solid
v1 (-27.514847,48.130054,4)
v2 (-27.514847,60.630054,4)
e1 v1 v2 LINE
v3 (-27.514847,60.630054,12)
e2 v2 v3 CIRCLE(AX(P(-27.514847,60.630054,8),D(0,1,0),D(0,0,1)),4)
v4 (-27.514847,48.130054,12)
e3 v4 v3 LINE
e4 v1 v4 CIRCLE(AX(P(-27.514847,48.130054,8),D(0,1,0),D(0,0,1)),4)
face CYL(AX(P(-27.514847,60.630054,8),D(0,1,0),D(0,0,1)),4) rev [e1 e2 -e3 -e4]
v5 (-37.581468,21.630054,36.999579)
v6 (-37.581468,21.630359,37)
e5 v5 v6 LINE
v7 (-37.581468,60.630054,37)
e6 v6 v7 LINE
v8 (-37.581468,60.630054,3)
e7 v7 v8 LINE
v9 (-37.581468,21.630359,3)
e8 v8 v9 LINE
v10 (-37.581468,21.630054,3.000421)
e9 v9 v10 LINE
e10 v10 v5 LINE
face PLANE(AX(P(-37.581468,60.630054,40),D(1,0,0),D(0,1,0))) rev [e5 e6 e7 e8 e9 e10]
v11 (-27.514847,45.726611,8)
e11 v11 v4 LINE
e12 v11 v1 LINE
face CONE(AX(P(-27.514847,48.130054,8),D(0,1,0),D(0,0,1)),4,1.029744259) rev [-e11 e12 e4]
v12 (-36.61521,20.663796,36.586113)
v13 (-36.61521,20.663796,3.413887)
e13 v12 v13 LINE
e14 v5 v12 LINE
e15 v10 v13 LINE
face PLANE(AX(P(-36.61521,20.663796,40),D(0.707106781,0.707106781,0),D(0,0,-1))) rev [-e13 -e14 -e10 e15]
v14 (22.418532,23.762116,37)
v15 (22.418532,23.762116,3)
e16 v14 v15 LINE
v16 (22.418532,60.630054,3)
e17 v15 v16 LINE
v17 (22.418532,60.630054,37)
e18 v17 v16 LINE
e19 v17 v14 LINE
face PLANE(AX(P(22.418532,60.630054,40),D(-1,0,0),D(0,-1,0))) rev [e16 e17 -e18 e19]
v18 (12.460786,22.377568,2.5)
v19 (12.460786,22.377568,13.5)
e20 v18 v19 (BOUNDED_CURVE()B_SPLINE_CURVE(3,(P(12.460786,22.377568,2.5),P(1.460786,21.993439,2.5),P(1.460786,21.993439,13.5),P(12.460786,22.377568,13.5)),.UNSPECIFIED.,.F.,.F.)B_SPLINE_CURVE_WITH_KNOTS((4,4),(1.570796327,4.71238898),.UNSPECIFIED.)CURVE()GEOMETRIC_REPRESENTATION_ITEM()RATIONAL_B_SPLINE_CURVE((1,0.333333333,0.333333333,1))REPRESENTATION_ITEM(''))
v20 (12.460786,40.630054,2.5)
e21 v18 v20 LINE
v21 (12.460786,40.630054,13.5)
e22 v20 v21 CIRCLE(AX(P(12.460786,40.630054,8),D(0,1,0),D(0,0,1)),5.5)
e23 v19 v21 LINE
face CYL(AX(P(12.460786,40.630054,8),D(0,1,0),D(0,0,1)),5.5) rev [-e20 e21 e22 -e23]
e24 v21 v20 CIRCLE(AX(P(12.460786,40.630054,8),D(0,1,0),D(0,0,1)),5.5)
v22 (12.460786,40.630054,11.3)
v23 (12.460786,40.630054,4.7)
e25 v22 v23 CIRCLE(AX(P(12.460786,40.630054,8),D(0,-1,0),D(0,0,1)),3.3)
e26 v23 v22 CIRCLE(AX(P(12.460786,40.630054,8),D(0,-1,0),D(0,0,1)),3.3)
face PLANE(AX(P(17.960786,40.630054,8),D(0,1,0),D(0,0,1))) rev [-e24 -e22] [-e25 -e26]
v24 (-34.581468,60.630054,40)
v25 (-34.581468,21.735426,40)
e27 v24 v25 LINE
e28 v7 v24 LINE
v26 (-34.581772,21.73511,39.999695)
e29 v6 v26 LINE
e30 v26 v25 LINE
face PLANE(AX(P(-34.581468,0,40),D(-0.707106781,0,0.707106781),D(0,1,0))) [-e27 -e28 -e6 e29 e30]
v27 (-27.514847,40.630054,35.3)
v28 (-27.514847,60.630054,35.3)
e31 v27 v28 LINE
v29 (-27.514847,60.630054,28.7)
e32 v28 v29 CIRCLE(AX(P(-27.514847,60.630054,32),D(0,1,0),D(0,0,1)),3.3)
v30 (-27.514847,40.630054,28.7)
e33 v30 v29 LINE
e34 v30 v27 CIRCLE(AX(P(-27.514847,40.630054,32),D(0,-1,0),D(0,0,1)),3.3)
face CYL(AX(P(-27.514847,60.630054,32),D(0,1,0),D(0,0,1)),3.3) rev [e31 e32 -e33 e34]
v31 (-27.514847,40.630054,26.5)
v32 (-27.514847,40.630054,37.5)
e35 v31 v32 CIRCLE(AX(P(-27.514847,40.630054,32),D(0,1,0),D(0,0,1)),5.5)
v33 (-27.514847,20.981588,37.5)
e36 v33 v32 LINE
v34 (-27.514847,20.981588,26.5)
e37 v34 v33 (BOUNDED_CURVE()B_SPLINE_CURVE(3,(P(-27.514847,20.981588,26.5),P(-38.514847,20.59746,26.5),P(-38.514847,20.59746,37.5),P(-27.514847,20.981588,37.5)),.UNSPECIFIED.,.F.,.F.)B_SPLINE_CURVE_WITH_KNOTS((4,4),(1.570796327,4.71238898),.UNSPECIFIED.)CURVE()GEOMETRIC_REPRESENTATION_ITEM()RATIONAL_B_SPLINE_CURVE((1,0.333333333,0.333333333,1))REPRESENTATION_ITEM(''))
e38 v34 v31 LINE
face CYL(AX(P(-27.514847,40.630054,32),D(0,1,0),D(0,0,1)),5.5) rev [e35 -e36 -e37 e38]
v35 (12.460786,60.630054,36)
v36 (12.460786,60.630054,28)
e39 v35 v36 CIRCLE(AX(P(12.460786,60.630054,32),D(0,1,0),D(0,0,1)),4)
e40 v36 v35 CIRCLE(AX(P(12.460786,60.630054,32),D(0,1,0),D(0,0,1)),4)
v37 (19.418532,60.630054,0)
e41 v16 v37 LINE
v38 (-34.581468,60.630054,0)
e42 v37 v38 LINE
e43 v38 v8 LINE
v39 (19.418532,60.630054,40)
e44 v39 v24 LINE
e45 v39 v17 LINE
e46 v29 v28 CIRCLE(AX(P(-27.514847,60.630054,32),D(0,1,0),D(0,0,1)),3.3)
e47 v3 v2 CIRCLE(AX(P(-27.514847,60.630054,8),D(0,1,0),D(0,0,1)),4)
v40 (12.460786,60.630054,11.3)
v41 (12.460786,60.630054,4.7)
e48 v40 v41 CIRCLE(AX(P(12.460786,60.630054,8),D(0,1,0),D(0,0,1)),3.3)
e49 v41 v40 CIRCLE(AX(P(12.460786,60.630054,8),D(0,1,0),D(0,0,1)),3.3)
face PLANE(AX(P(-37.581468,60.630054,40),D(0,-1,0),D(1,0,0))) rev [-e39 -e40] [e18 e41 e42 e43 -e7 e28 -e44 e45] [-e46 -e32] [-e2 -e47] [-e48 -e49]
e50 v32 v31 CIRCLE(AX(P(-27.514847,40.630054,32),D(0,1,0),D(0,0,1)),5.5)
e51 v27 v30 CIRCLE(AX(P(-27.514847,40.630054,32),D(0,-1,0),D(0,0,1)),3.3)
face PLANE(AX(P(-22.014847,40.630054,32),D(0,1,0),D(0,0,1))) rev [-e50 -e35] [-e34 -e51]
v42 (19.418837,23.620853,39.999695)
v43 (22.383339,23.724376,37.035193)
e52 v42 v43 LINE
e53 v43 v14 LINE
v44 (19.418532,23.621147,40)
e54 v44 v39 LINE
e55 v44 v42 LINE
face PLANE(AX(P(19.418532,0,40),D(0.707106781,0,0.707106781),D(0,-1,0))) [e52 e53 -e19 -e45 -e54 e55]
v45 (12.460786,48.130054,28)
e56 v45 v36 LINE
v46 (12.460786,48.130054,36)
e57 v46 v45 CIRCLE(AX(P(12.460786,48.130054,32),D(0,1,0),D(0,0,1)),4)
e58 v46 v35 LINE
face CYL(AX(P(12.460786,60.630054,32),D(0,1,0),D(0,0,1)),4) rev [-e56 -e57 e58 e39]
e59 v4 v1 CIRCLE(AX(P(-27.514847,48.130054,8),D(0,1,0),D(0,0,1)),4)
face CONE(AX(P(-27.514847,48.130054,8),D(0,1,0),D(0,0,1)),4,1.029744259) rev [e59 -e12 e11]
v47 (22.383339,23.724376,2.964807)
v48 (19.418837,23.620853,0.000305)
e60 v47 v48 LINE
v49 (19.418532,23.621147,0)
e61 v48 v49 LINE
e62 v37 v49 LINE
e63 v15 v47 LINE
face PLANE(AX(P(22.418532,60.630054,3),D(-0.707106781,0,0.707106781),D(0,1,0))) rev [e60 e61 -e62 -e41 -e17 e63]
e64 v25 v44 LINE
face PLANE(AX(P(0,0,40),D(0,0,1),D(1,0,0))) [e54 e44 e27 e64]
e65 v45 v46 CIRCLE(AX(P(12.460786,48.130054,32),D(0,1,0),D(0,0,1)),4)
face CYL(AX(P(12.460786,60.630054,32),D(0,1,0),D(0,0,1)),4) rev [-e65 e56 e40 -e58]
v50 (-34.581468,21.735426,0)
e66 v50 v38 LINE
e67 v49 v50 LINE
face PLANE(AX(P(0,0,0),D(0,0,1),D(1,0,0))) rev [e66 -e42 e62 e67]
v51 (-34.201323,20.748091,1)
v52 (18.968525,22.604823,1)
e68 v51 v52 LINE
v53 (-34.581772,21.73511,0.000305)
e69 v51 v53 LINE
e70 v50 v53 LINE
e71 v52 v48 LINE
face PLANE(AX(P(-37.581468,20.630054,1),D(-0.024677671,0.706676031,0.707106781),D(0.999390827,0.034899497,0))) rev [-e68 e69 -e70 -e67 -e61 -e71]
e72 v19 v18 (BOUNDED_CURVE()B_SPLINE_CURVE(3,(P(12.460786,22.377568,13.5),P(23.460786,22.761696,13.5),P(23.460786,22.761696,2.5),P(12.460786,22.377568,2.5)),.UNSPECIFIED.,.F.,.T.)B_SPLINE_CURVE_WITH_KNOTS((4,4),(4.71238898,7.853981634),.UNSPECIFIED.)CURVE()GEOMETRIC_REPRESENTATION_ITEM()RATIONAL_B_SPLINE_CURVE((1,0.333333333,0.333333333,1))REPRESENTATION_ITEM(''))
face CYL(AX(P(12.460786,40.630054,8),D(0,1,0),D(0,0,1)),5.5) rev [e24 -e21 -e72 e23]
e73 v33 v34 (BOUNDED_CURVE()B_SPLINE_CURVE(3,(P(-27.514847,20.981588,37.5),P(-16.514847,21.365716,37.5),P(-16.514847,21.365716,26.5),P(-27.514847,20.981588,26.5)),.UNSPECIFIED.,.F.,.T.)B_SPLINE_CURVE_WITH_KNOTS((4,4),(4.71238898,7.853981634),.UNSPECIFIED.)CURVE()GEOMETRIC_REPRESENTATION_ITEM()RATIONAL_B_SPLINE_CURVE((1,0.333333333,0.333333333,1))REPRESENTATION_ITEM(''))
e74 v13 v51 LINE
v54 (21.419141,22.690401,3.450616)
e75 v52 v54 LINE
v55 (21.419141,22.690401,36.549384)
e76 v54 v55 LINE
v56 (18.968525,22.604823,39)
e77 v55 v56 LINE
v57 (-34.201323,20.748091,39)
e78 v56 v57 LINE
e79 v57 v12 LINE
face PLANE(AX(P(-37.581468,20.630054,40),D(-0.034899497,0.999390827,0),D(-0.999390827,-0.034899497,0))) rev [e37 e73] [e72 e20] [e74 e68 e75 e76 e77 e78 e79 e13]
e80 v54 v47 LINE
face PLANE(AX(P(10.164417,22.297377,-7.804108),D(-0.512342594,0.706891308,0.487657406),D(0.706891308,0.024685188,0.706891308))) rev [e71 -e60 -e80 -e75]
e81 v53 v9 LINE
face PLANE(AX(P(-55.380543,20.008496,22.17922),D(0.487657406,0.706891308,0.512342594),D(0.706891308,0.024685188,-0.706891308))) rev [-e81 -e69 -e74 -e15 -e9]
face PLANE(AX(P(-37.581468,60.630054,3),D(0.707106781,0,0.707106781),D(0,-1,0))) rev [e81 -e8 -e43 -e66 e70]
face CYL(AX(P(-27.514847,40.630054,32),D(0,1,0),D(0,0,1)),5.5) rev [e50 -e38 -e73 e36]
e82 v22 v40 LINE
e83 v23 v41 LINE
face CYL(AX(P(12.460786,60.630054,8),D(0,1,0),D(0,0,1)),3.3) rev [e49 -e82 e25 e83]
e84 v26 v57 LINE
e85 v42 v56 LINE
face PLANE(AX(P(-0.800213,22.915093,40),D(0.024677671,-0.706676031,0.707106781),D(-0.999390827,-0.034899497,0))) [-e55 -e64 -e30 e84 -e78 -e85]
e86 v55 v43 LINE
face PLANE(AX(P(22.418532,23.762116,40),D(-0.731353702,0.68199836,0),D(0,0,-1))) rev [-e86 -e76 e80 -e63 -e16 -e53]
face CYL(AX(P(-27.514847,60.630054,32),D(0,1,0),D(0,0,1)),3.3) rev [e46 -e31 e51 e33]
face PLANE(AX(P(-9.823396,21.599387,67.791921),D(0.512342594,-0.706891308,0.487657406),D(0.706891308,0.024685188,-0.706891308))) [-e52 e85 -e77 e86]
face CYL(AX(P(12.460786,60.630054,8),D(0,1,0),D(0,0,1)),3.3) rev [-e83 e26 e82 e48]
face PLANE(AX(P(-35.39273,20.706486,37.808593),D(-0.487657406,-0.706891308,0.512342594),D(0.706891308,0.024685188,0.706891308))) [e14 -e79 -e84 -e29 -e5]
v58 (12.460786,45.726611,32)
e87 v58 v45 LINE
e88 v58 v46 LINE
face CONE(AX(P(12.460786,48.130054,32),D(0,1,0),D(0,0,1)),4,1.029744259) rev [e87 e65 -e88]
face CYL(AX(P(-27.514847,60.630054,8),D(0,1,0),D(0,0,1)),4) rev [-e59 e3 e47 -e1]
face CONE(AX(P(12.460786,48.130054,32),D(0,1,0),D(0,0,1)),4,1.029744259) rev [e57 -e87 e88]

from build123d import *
from OCP.BRepFilletAPI import BRepFilletAPI_MakeChamfer

# Parameters (mm, degrees)
BOSS_EXTRUDE1_DEPTH        = 40
CHAMFER1_SIZE              = 3
CHAMFER2_SIZE              = 1
CHAMFER2_SIZE2             = 0.96684652
CHAMFER2_SIZE2_2           = 1.036815955
CHAMFER2_SIZE2_3           = 0.976206784
CHAMFER2_SIZE2_4           = 1.025622313
HOLE2_D                    = 6.6
HOLE2_DEPTH                = 20
SKETCH11_W                 = 5.5
SKETCH11_H                 = 19.966257543
HOLE3_AT_2_COUNT           = 2
HOLE3_AT_2_PITCH           = 46.626722383
SIZE_MM_BLIND_HOLE_1_D     = 8
SIZE_MM_BLIND_HOLE_1_DEPTH = 12.5
SIZE_MM_BLIND_HOLE_1_TIP   = 2.403442476


with BuildPart() as part:
    # Sketch2 → Boss-Extrude1 (new body)
    with BuildSketch(Plane.XY):
        Polygon((-37.58146769, 20.630053858), (22.41853231, 22.725300027), (22.41853231, 60.630053858), (-37.58146769, 60.630053858), align=None)
    extrude(amount=BOSS_EXTRUDE1_DEPTH)

    # Chamfer1
    chamfer1_edges = [part.edges().sort_by_distance(p)[0] for p in [
        (22.41853231, 41.677676942, 40),
        (-37.58146769, 40.630053858, 40),
        (22.41853231, 41.677676942, 0),
        (-37.58146769, 40.630053858, 0),
    ]]
    chamfer(chamfer1_edges, length=CHAMFER1_SIZE)

    # Chamfer2: one chamfer whose edges measure the first distance from different faces: ONE call of the kernel's chamfer builder (chamfer() names one face for all edges)
    chamfer2_edges_1 = [part.edges().sort_by_distance(p)[0] for p in [
        (-37.58146769, 20.630053858, 20),
    ]]
    chamfer2_side_1 = [part.faces().sort_by_distance(p)[0] for p in [
        (-37.58146769, 40.630053858, 20),
    ]]
    chamfer2_edges_2 = [part.edges().sort_by_distance(p)[0] for p in [
        (-7.58146769, 21.677676942, 0),
        (-7.58146769, 21.677676942, 40),
    ]]
    chamfer2_edges_3 = [part.edges().sort_by_distance(p)[0] for p in [
        (22.41853231, 22.725300027, 20),
    ]]
    chamfer2_side_3 = [part.faces().sort_by_distance(p)[0] for p in [
        (-7.58146769, 21.677676942, 20),
    ]]
    chamfer2_edges_4 = [part.edges().sort_by_distance(p)[0] for p in [
        (-36.08146769, 20.682435012, 38.5),
    ]]
    chamfer2_side_4 = [part.faces().sort_by_distance(p)[0] for p in [
        (-36.082123313, 40.656232987, 38.499344377),
    ]]
    chamfer2_edges_5 = [part.edges().sort_by_distance(p)[0] for p in [
        (20.91853231, 22.672918873, 38.5),
    ]]
    chamfer2_side_5 = [part.faces().sort_by_distance(p)[0] for p in [
        (20.917842306, 41.651474317, 38.500690004),
    ]]
    chamfer2_edges_6 = [part.edges().sort_by_distance(p)[0] for p in [
        (20.91853231, 22.672918873, 1.5),
    ]]
    chamfer2_side_6 = [part.faces().sort_by_distance(p)[0] for p in [
        (20.917842306, 41.651474317, 1.499309996),
    ]]
    chamfer2_edges_7 = [part.edges().sort_by_distance(p)[0] for p in [
        (-36.08146769, 20.682435012, 1.5),
    ]]
    chamfer2_side_7 = [part.faces().sort_by_distance(p)[0] for p in [
        (-36.082123313, 40.656232987, 1.500655623),
    ]]
    chamfer2 = BRepFilletAPI_MakeChamfer(part.part.solid().wrapped)
    for e in chamfer2_edges_1:
        chamfer2.Add(CHAMFER2_SIZE, CHAMFER2_SIZE2, e.wrapped, chamfer2_side_1[0].wrapped)  # the first distance lies on this face
    for e in chamfer2_edges_2:
        chamfer2.Add(CHAMFER2_SIZE, e.wrapped)
    for e in chamfer2_edges_3:
        chamfer2.Add(CHAMFER2_SIZE, CHAMFER2_SIZE2_2, e.wrapped, chamfer2_side_3[0].wrapped)  # the first distance lies on this face
    for e in chamfer2_edges_4:
        chamfer2.Add(CHAMFER2_SIZE, CHAMFER2_SIZE2_3, e.wrapped, chamfer2_side_4[0].wrapped)  # the first distance lies on this face
    for e in chamfer2_edges_5:
        chamfer2.Add(CHAMFER2_SIZE, CHAMFER2_SIZE2_4, e.wrapped, chamfer2_side_5[0].wrapped)  # the first distance lies on this face
    for e in chamfer2_edges_6:
        chamfer2.Add(CHAMFER2_SIZE, CHAMFER2_SIZE2_4, e.wrapped, chamfer2_side_6[0].wrapped)  # the first distance lies on this face
    for e in chamfer2_edges_7:
        chamfer2.Add(CHAMFER2_SIZE, CHAMFER2_SIZE2_3, e.wrapped, chamfer2_side_7[0].wrapped)  # the first distance lies on this face
    add(Compound.cast(chamfer2.Shape()), mode=Mode.REPLACE)

    # Hole2
    with Locations(Plane(origin=(0, 60.630053858, 0), x_dir=(1, 0, 0), z_dir=(0, 1, 0))):
        with Locations((-27.514846728, -32), (12.460786352, -8)):
            Hole(HOLE2_D / 2, depth=HOLE2_DEPTH)

    # Sketch11 → Hole3 (revolve, cut)
    with BuildSketch(Plane(origin=(-27.514846728, 40.630053858, 32), x_dir=(0, 0, 1), z_dir=(1, 0, 0))):
        with Locations((2.75, 9.983128772)):
            Rectangle(SKETCH11_W, SKETCH11_H)
    hole3 = revolve(axis=Axis((-27.514846728, -69.369946142, 32), (0, 1, 0)), mode=Mode.SUBTRACT)

    # Hole3 at 2: Hole3 ×2
    with Locations(*[Vector(0.8573545605919571, 0, -0.514726293705861) * (i * HOLE3_AT_2_PITCH) for i in range(1, HOLE3_AT_2_COUNT)]):
        add(hole3, mode=Mode.SUBTRACT)

    # Size mm blind hole 1
    with Locations(Plane(origin=(0, 60.630053858, 0), x_dir=(1, 0, 0), z_dir=(0, 1, 0))):
        with Locations((-27.514846728, -8), (12.460786352, -32)):
            Hole(SIZE_MM_BLIND_HOLE_1_D / 2, depth=SIZE_MM_BLIND_HOLE_1_DEPTH)
            with Locations((0, 0, -(SIZE_MM_BLIND_HOLE_1_DEPTH + SIZE_MM_BLIND_HOLE_1_TIP / 2))):  # 118° drill point
                Cone(0, SIZE_MM_BLIND_HOLE_1_D / 2, SIZE_MM_BLIND_HOLE_1_TIP, mode=Mode.SUBTRACT)


solid = part.part
